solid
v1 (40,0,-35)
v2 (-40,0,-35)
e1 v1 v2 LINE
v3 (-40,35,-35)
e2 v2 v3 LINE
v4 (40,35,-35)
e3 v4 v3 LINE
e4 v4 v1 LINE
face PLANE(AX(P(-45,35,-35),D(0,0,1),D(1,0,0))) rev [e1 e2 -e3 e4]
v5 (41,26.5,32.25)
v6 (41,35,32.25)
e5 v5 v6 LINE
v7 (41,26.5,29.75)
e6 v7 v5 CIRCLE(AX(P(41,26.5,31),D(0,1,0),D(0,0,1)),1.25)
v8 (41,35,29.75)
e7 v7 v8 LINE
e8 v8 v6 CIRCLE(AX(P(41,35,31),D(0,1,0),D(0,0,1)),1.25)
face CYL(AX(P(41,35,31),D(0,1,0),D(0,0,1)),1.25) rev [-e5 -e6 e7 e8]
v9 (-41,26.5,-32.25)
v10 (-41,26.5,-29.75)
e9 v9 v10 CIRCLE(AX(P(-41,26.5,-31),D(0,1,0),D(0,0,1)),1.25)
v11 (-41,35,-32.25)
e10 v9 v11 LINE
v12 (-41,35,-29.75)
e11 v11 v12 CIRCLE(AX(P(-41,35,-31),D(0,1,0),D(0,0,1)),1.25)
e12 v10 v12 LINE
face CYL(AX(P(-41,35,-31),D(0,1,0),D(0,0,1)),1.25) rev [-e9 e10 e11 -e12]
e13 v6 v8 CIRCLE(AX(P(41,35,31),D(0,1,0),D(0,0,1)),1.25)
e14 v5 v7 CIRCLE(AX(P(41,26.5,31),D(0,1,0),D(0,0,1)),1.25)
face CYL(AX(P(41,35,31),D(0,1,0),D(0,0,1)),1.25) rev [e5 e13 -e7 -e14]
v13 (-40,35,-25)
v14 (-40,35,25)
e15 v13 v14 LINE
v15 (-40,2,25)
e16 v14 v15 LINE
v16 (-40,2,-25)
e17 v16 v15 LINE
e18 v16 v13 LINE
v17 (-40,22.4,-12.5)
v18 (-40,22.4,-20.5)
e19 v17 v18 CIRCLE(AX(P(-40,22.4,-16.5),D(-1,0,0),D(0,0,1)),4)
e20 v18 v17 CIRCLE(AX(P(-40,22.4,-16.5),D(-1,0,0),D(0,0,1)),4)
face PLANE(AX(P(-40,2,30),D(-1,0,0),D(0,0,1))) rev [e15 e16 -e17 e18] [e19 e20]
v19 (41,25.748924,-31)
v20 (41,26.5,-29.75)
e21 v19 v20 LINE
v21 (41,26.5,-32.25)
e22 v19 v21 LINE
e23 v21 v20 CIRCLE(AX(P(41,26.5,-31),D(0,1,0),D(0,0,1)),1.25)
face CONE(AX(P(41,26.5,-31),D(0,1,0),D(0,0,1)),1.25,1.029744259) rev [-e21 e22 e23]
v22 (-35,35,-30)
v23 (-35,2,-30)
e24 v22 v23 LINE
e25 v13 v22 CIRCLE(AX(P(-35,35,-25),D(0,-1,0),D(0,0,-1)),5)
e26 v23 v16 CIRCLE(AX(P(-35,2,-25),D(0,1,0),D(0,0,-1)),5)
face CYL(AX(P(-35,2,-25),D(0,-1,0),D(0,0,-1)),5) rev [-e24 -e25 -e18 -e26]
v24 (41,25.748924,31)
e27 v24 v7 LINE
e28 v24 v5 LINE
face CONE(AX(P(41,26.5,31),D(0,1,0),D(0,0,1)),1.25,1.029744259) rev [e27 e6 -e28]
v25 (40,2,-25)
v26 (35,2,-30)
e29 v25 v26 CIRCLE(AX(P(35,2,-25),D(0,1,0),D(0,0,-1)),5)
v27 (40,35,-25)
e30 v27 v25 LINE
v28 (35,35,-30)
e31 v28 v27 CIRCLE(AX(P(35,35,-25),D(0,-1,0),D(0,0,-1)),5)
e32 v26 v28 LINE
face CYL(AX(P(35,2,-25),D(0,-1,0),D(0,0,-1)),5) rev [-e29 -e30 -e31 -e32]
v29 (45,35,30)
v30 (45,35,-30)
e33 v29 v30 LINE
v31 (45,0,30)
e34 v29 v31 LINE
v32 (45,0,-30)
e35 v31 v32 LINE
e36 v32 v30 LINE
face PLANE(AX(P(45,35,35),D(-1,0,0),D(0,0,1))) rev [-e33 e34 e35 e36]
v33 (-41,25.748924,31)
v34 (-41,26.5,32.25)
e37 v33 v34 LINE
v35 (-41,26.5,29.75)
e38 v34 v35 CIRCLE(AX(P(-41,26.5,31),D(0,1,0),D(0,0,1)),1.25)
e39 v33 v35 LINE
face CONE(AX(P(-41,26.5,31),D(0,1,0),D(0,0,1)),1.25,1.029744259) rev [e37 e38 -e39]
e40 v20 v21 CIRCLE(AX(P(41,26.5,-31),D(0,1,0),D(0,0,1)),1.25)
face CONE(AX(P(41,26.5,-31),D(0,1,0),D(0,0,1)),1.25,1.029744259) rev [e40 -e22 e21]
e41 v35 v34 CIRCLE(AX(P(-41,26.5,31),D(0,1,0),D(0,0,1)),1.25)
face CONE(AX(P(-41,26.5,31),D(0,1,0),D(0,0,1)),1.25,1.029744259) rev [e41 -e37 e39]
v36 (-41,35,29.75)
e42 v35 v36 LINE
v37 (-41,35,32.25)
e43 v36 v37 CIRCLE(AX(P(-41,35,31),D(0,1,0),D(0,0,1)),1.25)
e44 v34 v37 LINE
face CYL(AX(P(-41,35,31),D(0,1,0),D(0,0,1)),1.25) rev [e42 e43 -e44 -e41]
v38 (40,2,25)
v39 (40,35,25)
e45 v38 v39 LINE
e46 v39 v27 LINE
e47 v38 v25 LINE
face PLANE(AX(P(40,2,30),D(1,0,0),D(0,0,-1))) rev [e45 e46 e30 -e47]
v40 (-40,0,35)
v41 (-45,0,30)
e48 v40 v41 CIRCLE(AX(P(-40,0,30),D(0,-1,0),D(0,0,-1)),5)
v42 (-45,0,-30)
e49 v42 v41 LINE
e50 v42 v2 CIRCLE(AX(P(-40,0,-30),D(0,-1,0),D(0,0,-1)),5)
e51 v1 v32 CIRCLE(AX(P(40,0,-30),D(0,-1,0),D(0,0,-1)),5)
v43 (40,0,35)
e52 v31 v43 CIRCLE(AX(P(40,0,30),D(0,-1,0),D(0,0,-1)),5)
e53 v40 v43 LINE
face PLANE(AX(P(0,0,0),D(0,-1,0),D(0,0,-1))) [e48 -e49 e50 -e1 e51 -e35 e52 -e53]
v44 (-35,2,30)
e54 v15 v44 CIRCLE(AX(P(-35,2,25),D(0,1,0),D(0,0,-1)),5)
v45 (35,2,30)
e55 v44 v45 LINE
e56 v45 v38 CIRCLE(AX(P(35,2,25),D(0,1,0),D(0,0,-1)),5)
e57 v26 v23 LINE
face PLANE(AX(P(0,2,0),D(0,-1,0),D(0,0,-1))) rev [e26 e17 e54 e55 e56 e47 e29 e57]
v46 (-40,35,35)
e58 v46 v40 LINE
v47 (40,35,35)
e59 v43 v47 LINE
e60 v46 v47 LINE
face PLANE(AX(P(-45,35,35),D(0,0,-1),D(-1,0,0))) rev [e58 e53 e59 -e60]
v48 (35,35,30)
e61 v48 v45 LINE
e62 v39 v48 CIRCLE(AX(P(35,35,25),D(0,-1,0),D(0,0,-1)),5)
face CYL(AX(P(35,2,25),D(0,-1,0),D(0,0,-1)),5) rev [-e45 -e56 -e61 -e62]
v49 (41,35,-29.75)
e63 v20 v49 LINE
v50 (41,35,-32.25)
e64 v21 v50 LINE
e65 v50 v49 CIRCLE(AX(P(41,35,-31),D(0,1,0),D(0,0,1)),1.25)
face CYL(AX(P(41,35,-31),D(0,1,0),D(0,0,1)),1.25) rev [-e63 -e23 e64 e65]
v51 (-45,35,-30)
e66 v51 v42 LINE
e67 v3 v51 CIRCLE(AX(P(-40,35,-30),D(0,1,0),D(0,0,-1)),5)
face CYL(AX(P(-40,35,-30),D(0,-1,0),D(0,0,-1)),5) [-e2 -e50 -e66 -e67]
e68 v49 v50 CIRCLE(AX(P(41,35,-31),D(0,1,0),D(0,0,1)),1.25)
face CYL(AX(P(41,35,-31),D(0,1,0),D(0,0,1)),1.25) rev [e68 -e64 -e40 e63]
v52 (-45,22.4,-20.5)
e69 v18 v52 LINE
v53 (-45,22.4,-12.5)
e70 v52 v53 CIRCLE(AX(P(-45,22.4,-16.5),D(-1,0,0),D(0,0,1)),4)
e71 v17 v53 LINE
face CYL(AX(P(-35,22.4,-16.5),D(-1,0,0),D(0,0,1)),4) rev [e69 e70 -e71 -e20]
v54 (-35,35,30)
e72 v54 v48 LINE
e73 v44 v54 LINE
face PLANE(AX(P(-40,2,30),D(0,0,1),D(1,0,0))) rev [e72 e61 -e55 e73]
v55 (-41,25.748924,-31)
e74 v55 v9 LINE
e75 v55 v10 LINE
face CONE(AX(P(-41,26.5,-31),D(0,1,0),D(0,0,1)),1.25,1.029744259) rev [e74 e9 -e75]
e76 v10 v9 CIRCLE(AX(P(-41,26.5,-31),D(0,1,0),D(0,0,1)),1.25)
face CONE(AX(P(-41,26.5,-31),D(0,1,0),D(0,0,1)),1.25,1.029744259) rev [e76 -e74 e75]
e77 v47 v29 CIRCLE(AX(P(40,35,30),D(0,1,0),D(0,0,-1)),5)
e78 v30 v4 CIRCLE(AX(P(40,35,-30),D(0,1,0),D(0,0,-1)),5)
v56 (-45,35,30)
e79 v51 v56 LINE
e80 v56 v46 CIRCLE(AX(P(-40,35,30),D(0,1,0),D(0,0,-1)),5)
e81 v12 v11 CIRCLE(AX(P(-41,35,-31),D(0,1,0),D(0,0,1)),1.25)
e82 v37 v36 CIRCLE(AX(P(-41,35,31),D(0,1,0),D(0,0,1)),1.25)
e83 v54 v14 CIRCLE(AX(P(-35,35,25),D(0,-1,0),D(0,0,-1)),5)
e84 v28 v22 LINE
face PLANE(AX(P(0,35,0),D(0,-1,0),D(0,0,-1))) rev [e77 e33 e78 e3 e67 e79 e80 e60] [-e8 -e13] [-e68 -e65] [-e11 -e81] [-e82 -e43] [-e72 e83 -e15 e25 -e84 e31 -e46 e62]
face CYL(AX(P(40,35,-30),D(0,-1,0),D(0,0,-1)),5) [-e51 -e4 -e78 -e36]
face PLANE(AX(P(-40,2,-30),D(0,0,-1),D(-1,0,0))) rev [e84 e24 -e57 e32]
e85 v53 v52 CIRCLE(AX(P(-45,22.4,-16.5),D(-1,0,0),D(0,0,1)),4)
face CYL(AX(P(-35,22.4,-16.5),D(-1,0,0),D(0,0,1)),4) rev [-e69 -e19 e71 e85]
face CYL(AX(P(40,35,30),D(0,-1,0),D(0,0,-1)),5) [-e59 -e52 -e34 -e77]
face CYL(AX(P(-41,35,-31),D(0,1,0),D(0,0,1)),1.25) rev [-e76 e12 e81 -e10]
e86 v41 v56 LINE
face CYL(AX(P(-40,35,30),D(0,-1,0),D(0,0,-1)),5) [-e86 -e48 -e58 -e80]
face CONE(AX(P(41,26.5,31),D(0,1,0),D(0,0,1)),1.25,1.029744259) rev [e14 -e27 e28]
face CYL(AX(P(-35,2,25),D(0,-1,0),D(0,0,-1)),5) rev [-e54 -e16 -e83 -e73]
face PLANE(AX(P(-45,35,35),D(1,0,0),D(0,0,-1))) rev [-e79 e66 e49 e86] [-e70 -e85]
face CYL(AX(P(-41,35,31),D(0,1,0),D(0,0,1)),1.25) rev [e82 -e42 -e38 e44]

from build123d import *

# Parameters (mm, degrees)
SKETCH1_W             = 90
SKETCH1_H             = 70
BOSS_EXTRUDE1_DEPTH   = 35
SKETCH2_W             = 80
SKETCH2_H             = 60
CUT_EXTRUDE1_DEPTH    = 33
FILLET1_R             = 5
M3_TAPPED_HOLE1_D     = 2.5
M3_TAPPED_HOLE1_DEPTH = 8.5
M3_TAPPED_HOLE1_TIP   = 0.751075774
SKETCH7_R             = 4
CUT_EXTRUDE2_DEPTH    = 10


with BuildPart() as part:
    # Sketch1 → Boss-Extrude1 (new body)
    with BuildSketch(Plane(origin=(0, 0, 0), x_dir=(1, 0, 0), z_dir=(0, 1, 0))):
        Rectangle(SKETCH1_W, SKETCH1_H)
    extrude(amount=BOSS_EXTRUDE1_DEPTH)

    # Sketch2 → Cut-Extrude1 (cut)
    with BuildSketch(Plane(origin=(0, 35, 0), x_dir=(1, 0, 0), z_dir=(0, 1, 0))):
        Rectangle(SKETCH2_W, SKETCH2_H)
    extrude(amount=-CUT_EXTRUDE1_DEPTH, mode=Mode.SUBTRACT)

    # Fillet1
    fillet1_edges = [part.edges().sort_by_distance(p)[0] for p in [
        (40, 18.5, -30),
        (40, 18.5, 30),
        (-40, 18.5, 30),
        (-40, 18.5, -30),
        (45, 17.5, 35),
        (-45, 17.5, 35),
        (-45, 17.5, -35),
        (45, 17.5, -35),
    ]]
    fillet(fillet1_edges, radius=FILLET1_R)

    # M3 Tapped Hole1
    with Locations(Plane(origin=(0, 35, 0), x_dir=(1, 0, 0), z_dir=(0, 1, 0))):
        with Locations((-41, 31), (41, 31), (41, -31), (-41, -31)):
            Hole(M3_TAPPED_HOLE1_D / 2, depth=M3_TAPPED_HOLE1_DEPTH)
            with Locations((0, 0, -(M3_TAPPED_HOLE1_DEPTH + M3_TAPPED_HOLE1_TIP / 2))):  # 118° drill point
                Cone(0, M3_TAPPED_HOLE1_D / 2, M3_TAPPED_HOLE1_TIP, mode=Mode.SUBTRACT)

    # Sketch7 → Cut-Extrude2 (cut)
    with BuildSketch(Plane.ZY.offset(45)):
        with Locations((-16.5, 22.4)):
            Circle(SKETCH7_R)
    extrude(amount=-CUT_EXTRUDE2_DEPTH, mode=Mode.SUBTRACT)


solid = part.part
